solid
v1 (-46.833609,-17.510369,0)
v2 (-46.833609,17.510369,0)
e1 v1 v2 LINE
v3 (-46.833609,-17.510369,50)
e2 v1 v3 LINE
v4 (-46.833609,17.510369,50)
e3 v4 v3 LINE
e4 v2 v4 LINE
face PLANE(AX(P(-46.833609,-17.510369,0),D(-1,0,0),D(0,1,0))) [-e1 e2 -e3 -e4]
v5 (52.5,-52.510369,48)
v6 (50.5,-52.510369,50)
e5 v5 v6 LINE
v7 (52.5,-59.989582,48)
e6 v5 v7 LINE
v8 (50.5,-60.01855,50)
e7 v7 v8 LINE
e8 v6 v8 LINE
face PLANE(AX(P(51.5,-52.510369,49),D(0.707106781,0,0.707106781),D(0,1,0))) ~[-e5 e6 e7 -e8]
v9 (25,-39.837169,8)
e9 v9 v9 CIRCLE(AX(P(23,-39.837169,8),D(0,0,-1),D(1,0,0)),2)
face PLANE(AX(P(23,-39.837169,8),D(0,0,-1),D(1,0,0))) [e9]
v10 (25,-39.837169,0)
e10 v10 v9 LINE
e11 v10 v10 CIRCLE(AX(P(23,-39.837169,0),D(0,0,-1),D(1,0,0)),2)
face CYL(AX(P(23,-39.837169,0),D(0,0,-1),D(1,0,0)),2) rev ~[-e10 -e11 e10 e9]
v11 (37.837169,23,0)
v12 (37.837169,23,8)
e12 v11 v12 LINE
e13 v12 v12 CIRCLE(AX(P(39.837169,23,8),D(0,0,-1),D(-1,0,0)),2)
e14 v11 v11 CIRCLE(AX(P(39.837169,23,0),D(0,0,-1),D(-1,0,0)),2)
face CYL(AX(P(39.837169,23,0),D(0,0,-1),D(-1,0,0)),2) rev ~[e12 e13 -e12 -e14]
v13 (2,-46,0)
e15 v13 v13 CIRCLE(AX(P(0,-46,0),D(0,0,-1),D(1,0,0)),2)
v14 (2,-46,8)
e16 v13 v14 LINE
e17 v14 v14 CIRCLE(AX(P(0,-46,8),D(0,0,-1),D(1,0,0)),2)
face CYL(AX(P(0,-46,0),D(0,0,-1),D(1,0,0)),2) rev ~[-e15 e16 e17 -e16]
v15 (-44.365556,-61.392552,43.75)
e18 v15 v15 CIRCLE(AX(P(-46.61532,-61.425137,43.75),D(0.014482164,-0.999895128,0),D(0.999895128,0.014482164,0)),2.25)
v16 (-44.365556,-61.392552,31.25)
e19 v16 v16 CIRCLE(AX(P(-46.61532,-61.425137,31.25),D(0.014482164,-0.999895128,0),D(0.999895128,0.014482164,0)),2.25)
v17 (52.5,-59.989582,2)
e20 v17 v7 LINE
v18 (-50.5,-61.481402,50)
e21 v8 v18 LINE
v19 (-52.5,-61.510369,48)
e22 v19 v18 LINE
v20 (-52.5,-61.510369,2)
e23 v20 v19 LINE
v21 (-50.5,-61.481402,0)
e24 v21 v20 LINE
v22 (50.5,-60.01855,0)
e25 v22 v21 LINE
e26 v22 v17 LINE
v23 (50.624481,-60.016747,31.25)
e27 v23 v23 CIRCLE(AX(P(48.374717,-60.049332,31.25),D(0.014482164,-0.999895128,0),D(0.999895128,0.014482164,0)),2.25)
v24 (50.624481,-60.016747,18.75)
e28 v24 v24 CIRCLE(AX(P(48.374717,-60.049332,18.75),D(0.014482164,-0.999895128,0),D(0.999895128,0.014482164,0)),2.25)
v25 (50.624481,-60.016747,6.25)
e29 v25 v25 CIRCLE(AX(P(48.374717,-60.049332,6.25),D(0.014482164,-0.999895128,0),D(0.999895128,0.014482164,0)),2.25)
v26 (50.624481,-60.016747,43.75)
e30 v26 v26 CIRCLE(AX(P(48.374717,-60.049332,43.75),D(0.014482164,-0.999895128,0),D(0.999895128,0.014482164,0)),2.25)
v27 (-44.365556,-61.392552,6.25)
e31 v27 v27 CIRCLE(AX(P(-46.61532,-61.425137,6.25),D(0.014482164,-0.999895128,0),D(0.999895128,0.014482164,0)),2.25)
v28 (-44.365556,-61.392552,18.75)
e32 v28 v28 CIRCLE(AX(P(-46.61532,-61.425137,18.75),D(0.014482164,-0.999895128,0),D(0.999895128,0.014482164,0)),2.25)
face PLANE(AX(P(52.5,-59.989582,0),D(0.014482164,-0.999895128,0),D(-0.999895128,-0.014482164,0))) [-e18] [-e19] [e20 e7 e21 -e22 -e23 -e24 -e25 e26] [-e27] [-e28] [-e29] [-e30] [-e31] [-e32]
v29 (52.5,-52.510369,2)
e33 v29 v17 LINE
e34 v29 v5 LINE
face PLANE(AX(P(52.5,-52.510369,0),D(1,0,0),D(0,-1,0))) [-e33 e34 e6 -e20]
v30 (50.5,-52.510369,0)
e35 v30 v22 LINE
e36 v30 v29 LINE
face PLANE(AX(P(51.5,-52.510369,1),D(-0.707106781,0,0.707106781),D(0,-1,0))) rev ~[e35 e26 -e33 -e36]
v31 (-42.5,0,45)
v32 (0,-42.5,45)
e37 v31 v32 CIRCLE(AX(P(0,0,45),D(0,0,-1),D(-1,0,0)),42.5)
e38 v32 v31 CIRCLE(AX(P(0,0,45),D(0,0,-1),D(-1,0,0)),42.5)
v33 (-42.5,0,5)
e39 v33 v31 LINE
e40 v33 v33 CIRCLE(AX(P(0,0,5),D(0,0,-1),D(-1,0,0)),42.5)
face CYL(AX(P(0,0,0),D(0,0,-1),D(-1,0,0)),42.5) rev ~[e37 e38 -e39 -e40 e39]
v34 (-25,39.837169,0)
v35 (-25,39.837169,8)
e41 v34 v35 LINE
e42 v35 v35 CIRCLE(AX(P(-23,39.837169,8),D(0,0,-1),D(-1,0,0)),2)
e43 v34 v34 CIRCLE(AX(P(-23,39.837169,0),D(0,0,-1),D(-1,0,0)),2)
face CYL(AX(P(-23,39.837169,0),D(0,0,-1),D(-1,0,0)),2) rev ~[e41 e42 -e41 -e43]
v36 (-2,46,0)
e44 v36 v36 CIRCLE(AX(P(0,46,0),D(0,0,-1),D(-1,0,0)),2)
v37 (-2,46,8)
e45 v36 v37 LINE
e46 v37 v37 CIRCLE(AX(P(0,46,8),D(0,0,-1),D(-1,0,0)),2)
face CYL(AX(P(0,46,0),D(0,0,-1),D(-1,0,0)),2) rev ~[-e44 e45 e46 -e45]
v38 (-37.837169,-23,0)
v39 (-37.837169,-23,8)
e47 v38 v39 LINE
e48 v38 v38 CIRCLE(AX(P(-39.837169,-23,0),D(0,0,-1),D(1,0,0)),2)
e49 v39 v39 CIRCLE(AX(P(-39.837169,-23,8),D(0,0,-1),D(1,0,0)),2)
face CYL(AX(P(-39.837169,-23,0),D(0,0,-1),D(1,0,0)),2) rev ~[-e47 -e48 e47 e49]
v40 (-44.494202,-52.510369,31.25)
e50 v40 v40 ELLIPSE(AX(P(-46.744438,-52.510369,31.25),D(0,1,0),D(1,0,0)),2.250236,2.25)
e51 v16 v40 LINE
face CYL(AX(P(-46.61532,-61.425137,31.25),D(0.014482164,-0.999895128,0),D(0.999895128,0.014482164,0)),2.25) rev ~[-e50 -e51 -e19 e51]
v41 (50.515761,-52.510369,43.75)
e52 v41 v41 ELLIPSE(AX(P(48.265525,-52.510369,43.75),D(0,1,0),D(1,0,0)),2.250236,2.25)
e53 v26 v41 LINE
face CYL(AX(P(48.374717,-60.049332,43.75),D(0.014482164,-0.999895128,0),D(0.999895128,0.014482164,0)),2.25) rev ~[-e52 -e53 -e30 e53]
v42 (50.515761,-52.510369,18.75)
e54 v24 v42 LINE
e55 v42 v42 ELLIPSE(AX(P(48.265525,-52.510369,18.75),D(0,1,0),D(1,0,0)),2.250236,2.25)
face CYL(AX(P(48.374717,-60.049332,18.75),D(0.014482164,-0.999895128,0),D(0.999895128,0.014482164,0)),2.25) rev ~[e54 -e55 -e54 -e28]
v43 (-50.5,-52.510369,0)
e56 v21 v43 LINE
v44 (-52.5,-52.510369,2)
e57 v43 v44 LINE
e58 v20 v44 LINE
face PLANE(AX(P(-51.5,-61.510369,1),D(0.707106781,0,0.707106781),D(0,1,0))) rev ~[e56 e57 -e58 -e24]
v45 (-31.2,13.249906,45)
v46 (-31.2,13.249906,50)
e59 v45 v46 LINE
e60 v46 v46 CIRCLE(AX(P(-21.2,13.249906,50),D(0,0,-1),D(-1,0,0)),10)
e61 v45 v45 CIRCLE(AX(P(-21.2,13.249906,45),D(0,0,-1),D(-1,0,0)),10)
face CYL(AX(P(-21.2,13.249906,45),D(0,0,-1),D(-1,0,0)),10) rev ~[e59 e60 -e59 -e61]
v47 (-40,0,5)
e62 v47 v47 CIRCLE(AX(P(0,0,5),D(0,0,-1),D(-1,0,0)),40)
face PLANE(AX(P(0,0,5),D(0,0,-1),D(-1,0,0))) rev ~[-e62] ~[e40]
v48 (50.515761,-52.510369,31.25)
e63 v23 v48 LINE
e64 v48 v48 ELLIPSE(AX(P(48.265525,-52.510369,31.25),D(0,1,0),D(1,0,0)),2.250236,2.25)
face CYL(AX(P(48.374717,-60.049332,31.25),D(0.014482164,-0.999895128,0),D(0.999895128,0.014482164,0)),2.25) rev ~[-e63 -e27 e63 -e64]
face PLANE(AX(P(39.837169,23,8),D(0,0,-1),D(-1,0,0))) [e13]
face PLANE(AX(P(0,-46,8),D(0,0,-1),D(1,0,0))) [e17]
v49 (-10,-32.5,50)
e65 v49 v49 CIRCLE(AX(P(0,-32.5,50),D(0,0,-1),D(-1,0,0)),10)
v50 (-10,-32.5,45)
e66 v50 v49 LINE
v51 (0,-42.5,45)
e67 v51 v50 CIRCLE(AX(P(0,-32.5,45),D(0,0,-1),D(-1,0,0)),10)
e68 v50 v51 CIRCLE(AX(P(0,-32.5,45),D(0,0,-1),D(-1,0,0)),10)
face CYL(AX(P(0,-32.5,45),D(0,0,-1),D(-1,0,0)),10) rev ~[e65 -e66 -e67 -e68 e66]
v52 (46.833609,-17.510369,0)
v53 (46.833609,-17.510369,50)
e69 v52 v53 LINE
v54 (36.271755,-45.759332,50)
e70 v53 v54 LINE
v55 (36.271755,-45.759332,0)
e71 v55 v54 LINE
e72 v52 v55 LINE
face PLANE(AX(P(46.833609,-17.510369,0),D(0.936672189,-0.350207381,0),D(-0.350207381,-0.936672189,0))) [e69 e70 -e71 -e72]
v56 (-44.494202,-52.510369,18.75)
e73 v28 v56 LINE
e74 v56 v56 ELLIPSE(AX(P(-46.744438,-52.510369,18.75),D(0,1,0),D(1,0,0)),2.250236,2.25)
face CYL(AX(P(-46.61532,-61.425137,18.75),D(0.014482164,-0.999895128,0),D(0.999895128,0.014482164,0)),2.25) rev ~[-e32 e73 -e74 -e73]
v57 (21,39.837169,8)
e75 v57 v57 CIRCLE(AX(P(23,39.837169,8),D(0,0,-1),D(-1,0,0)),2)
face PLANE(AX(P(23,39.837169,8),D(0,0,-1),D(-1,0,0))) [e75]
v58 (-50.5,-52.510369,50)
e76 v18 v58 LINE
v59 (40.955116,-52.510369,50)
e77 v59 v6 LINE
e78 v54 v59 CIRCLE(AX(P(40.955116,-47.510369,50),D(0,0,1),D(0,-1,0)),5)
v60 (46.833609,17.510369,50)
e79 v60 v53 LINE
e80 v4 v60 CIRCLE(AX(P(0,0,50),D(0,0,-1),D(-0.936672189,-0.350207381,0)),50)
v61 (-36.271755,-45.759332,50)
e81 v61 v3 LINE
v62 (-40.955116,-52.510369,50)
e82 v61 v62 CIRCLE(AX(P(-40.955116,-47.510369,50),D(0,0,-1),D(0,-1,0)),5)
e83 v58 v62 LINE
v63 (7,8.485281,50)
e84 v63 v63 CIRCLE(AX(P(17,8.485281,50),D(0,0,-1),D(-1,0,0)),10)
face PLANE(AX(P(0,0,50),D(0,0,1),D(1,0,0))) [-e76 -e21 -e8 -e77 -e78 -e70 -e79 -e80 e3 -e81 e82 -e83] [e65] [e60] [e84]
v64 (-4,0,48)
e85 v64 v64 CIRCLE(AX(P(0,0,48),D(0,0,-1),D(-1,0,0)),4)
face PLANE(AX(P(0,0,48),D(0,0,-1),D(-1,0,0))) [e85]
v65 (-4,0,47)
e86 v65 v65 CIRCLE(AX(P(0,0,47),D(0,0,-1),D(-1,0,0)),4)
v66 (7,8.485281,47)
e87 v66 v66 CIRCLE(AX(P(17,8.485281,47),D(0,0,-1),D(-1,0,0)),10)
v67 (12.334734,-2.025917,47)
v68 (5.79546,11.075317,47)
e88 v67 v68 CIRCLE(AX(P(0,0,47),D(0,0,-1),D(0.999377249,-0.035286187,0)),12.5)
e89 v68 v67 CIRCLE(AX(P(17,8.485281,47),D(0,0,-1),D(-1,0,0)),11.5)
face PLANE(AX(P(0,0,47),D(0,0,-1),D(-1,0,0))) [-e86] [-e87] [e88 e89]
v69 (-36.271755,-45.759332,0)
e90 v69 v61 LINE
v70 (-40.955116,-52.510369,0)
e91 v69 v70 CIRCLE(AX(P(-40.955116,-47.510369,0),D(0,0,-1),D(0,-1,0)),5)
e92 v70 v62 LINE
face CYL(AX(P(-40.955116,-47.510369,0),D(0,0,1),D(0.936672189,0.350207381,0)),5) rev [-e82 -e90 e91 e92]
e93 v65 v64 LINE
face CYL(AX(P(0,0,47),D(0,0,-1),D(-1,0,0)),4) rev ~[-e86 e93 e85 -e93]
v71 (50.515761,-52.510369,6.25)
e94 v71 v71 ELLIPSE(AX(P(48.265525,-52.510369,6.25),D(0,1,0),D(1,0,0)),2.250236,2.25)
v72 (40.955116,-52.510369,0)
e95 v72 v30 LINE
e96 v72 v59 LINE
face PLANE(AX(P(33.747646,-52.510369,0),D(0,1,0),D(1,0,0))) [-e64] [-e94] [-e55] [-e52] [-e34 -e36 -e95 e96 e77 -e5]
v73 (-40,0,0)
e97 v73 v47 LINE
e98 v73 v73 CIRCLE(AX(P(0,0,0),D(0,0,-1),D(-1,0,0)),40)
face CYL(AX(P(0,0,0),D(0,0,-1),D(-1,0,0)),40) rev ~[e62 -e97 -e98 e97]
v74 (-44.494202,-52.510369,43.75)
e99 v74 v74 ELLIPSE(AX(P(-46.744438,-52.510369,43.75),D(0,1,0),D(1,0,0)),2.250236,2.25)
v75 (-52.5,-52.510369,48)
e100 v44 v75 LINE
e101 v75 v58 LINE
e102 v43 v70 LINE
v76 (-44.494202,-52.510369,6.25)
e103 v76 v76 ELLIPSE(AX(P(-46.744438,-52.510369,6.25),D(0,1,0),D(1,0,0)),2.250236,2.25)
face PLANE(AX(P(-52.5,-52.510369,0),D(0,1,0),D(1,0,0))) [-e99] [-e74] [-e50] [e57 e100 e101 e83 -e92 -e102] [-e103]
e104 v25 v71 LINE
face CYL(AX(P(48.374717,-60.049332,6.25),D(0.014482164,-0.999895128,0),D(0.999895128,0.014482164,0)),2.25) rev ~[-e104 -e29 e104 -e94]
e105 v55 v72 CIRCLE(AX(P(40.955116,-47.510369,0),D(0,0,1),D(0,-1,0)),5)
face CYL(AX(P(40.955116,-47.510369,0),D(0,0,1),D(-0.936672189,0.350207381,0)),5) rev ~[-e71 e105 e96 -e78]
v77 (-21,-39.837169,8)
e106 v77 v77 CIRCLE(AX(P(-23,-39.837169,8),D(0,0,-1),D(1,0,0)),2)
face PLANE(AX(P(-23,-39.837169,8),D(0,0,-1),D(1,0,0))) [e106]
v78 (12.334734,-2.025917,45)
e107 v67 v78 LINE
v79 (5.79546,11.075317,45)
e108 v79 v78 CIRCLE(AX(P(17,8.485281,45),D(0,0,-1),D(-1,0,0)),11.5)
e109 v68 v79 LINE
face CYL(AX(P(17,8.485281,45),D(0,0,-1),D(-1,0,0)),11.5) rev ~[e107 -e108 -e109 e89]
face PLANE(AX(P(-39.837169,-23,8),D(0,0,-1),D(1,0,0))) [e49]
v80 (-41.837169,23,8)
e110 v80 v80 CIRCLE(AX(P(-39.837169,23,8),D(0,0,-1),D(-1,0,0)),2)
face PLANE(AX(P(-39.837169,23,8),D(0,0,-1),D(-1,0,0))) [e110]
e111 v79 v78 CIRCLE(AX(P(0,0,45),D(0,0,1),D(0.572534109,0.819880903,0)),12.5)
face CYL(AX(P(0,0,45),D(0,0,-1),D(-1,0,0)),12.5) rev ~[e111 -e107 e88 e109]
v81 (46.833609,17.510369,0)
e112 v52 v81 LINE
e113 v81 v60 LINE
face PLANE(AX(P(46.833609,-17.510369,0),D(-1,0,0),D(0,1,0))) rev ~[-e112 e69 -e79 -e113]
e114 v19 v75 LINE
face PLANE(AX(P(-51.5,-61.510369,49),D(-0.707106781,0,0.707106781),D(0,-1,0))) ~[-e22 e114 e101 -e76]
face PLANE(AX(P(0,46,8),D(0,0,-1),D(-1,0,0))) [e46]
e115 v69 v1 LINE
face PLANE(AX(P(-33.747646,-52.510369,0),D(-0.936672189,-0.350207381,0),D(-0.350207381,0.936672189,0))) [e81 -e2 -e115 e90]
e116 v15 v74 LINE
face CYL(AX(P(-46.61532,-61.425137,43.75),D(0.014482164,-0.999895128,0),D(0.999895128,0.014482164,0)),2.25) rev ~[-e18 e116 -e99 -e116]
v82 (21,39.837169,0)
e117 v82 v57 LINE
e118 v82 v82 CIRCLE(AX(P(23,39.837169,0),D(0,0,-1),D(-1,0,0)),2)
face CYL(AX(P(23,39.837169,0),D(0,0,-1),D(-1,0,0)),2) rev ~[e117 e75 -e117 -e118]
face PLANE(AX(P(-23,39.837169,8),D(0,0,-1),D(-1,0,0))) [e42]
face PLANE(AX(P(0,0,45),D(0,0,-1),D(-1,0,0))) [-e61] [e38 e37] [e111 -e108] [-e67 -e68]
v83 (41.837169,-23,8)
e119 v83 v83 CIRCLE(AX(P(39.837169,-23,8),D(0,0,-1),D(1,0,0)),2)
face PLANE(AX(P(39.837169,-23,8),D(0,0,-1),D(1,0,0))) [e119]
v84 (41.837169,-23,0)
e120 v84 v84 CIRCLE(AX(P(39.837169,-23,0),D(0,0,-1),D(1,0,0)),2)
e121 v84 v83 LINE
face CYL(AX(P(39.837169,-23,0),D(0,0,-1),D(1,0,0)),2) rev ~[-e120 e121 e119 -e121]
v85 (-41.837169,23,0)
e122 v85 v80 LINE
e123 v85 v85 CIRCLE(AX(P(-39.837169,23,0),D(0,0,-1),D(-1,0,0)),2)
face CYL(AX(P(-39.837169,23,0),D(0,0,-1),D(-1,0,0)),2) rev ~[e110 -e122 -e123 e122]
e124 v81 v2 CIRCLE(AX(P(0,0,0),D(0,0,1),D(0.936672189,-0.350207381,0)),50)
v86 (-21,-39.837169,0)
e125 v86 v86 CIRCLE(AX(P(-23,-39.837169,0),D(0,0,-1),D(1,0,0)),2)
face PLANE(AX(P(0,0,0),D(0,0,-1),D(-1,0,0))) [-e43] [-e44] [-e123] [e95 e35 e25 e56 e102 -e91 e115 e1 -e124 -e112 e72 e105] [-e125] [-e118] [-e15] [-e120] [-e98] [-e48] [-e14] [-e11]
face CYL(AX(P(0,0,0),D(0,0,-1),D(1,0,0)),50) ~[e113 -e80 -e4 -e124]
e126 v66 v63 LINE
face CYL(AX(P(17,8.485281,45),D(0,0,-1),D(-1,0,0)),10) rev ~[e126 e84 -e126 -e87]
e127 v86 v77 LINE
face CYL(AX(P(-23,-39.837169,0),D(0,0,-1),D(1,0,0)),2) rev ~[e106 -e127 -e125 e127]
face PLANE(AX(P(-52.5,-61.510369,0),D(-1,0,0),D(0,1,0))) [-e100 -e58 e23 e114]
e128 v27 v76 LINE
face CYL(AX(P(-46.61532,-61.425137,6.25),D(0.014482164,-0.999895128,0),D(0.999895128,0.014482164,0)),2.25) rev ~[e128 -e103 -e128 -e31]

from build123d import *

# Parameters (mm, degrees)
SKETCH1_R           = 50
BOSS_EXTRUDE1_DEPTH = 50
SKETCH2_R           = 42.5
CUT_EXTRUDE1_DEPTH  = 45
SKETCH3_R           = 12.5
CUT_EXTRUDE2_DEPTH  = 2
SKETCH4_R           = 10
CUT_EXTRUDE3_DEPTH  = 84.815273071
BOSS_EXTRUDE2_DEPTH = 50
CUT_EXTRUDE4_DEPTH  = 96.077733998
SKETCH7_R           = 2.25
CUT_EXTRUDE5_DEPTH  = 20
FILLET1_R           = 5
FILLET2_R           = 5
CHAMFER1_SIZE       = 2
SKETCH8_R           = 4
CUT_EXTRUDE6_DEPTH  = 1
SKETCH9_R           = 11.5
CUT_EXTRUDE8_DEPTH  = 2
SKETCH10_R          = 42.5
SKETCH10_R_2        = 40
BOSS_EXTRUDE3_DEPTH = 5
SKETCH11_R          = 2
CUT_EXTRUDE9_DEPTH  = 8


with BuildPart() as part:
    # Sketch1 → Boss-Extrude1 (new body)
    with BuildSketch(Plane.XY):
        Circle(SKETCH1_R)
    extrude(amount=BOSS_EXTRUDE1_DEPTH)

    # Sketch2 → Cut-Extrude1 (cut)
    with BuildSketch(Plane(origin=(0, 0, 0), x_dir=(-1, 0, 0), z_dir=(0, 0, -1))):
        Circle(SKETCH2_R)
    extrude(amount=-CUT_EXTRUDE1_DEPTH, mode=Mode.SUBTRACT)

    # Sketch3 → Cut-Extrude2 (cut)
    with BuildSketch(Plane(origin=(0, 0, 45), x_dir=(-1, 0, 0), z_dir=(0, 0, -1))):
        Circle(SKETCH3_R)
    extrude(amount=-CUT_EXTRUDE2_DEPTH, mode=Mode.SUBTRACT)

    # Sketch4 → Cut-Extrude3 (cut, through all)
    with BuildSketch(Plane(origin=(0, 0, 45), x_dir=(-1, 0, 0), z_dir=(0, 0, -1))):
        with Locations((-17, 8.485281374)):
            Circle(SKETCH4_R)
        with Locations((21.2, 13.24990566)):
            Circle(SKETCH4_R)
        with Locations((0, -32.5)):
            Circle(SKETCH4_R)
    extrude(amount=-CUT_EXTRUDE3_DEPTH, mode=Mode.SUBTRACT)

    # Sketch5 → Boss-Extrude2 (add)
    with BuildSketch(Plane(origin=(0, 0, 0), x_dir=(-1, 0, 0), z_dir=(0, 0, -1))):
        with BuildLine():
            Line((-46.833609462, -17.510369063), (-33.74764568, -52.510369063))
            Line((-33.74764568, -52.510369063), (-52.5, -52.510369063))
            Line((-52.5, -52.510369063), (-52.5, -59.989582371))
            Line((-52.5, -59.989582371), (52.5, -61.510369063))
            Line((52.5, -61.510369063), (52.5, -52.510369063))
            Line((52.5, -52.510369063), (33.74764568, -52.510369063))
            Line((33.74764568, -52.510369063), (46.833609462, -17.510369063))
            ThreePointArc((46.833609462, -17.510369063), (0, -50), (-46.833609462, -17.510369063))
        make_face()
    extrude(amount=-BOSS_EXTRUDE2_DEPTH)

    # Sketch6 → Cut-Extrude4 (cut, through all)
    with BuildSketch(Plane(origin=(0, 0, 0), x_dir=(-1, 0, 0), z_dir=(0, 0, -1))):
        with BuildLine():
            Line((-46.833609462, -17.510369063), (-46.833609462, 17.510369063))
            ThreePointArc((-46.833609462, 17.510369063), (-50, 0), (-46.833609462, -17.510369063))
        make_face()
        with BuildLine():
            Line((46.833609462, -17.510369063), (46.833609462, 17.510369063))
            ThreePointArc((46.833609462, 17.510369063), (50, 0), (46.833609462, -17.510369063))
        make_face()
    extrude(amount=-CUT_EXTRUDE4_DEPTH, mode=Mode.SUBTRACT)

    # Sketch7 → Cut-Extrude5 (cut)
    with BuildSketch(Plane(origin=(0.879698836, -60.737234438, 0), x_dir=(0.9998951279661363, 0.014482163843290402, 0), z_dir=(0.014482163843290404, -0.9998951279661364, 0))):
        with Locations((-47.5, 43.75)):
            Circle(SKETCH7_R)
        with Locations((-47.5, 31.25)):
            Circle(SKETCH7_R)
        with Locations((47.5, 31.25)):
            Circle(SKETCH7_R)
        with Locations((47.5, 43.75)):
            Circle(SKETCH7_R)
        with Locations((47.5, 18.75)):
            Circle(SKETCH7_R)
        with Locations((47.5, 6.25)):
            Circle(SKETCH7_R)
        with Locations((-47.5, 18.75)):
            Circle(SKETCH7_R)
        with Locations((-47.5, 6.25)):
            Circle(SKETCH7_R)
    extrude(amount=-CUT_EXTRUDE5_DEPTH, mode=Mode.SUBTRACT)

    # Fillet1
    fillet1_edges = [part.edges().sort_by_distance(p)[0] for p in [
        (33.74764568, -52.510369063, 25),
    ]]
    fillet(fillet1_edges, radius=FILLET1_R)

    # Fillet2
    fillet2_edges = [part.edges().sort_by_distance(p)[0] for p in [
        (-33.74764568, -52.510369063, 25),
    ]]
    fillet(fillet2_edges, radius=FILLET2_R)

    # Chamfer1
    chamfer1_edges = [part.edges().sort_by_distance(p)[0] for p in [
        (-52.5, -57.010369063, 50),
        (52.5, -56.249975717, 50),
        (52.5, -56.249975717, 0),
        (-52.5, -57.010369063, 0),
    ]]
    chamfer(chamfer1_edges, length=CHAMFER1_SIZE)

    # Sketch8 → Cut-Extrude6 (cut)
    with BuildSketch(Plane(origin=(0, 0, 47), x_dir=(-1, 0, 0), z_dir=(0, 0, -1))):
        Circle(SKETCH8_R)
    extrude(amount=-CUT_EXTRUDE6_DEPTH, mode=Mode.SUBTRACT)

    # Sketch9 → Cut-Extrude8 (cut)
    with BuildSketch(Plane(origin=(0, 0, 45), x_dir=(-1, 0, 0), z_dir=(0, 0, -1))):
        with Locations((-17, 8.485281374)):
            Circle(SKETCH9_R)
    extrude(amount=-CUT_EXTRUDE8_DEPTH, mode=Mode.SUBTRACT)

    # Sketch10 → Boss-Extrude3 (add)
    with BuildSketch(Plane(origin=(0, 0, 0), x_dir=(-1, 0, 0), z_dir=(0, 0, -1))):
        Circle(SKETCH10_R)
        Circle(SKETCH10_R_2, mode=Mode.SUBTRACT)
    extrude(amount=-BOSS_EXTRUDE3_DEPTH)

    # Sketch11 → Cut-Extrude9 (cut)
    with BuildSketch(Plane(origin=(0, 0, 0), x_dir=(-1, 0, 0), z_dir=(0, 0, -1))):
        with Locations((0, 46)):
            Circle(SKETCH11_R)
        with Locations((23, 39.837168574)):
            Circle(SKETCH11_R)
        with Locations((39.837168574, 23)):
            Circle(SKETCH11_R)
        with Locations((-23, 39.837168574)):
            Circle(SKETCH11_R)
        with Locations((-39.837168574, 23)):
            Circle(SKETCH11_R)
        with Locations(Location((39.837168574, -23, 0), (0, 0, 180))):
            Circle(SKETCH11_R)
        with Locations(Location((23, -39.837168574, 0), (0, 0, 180))):
            Circle(SKETCH11_R)
        with Locations(Location((0, -46, 0), (0, 0, 180))):
            Circle(SKETCH11_R)
        with Locations(Location((-23, -39.837168574, 0), (0, 0, 180))):
            Circle(SKETCH11_R)
        with Locations(Location((-39.837168574, -23, 0), (0, 0, 180))):
            Circle(SKETCH11_R)
    extrude(amount=-CUT_EXTRUDE9_DEPTH, mode=Mode.SUBTRACT)


solid = part.part
